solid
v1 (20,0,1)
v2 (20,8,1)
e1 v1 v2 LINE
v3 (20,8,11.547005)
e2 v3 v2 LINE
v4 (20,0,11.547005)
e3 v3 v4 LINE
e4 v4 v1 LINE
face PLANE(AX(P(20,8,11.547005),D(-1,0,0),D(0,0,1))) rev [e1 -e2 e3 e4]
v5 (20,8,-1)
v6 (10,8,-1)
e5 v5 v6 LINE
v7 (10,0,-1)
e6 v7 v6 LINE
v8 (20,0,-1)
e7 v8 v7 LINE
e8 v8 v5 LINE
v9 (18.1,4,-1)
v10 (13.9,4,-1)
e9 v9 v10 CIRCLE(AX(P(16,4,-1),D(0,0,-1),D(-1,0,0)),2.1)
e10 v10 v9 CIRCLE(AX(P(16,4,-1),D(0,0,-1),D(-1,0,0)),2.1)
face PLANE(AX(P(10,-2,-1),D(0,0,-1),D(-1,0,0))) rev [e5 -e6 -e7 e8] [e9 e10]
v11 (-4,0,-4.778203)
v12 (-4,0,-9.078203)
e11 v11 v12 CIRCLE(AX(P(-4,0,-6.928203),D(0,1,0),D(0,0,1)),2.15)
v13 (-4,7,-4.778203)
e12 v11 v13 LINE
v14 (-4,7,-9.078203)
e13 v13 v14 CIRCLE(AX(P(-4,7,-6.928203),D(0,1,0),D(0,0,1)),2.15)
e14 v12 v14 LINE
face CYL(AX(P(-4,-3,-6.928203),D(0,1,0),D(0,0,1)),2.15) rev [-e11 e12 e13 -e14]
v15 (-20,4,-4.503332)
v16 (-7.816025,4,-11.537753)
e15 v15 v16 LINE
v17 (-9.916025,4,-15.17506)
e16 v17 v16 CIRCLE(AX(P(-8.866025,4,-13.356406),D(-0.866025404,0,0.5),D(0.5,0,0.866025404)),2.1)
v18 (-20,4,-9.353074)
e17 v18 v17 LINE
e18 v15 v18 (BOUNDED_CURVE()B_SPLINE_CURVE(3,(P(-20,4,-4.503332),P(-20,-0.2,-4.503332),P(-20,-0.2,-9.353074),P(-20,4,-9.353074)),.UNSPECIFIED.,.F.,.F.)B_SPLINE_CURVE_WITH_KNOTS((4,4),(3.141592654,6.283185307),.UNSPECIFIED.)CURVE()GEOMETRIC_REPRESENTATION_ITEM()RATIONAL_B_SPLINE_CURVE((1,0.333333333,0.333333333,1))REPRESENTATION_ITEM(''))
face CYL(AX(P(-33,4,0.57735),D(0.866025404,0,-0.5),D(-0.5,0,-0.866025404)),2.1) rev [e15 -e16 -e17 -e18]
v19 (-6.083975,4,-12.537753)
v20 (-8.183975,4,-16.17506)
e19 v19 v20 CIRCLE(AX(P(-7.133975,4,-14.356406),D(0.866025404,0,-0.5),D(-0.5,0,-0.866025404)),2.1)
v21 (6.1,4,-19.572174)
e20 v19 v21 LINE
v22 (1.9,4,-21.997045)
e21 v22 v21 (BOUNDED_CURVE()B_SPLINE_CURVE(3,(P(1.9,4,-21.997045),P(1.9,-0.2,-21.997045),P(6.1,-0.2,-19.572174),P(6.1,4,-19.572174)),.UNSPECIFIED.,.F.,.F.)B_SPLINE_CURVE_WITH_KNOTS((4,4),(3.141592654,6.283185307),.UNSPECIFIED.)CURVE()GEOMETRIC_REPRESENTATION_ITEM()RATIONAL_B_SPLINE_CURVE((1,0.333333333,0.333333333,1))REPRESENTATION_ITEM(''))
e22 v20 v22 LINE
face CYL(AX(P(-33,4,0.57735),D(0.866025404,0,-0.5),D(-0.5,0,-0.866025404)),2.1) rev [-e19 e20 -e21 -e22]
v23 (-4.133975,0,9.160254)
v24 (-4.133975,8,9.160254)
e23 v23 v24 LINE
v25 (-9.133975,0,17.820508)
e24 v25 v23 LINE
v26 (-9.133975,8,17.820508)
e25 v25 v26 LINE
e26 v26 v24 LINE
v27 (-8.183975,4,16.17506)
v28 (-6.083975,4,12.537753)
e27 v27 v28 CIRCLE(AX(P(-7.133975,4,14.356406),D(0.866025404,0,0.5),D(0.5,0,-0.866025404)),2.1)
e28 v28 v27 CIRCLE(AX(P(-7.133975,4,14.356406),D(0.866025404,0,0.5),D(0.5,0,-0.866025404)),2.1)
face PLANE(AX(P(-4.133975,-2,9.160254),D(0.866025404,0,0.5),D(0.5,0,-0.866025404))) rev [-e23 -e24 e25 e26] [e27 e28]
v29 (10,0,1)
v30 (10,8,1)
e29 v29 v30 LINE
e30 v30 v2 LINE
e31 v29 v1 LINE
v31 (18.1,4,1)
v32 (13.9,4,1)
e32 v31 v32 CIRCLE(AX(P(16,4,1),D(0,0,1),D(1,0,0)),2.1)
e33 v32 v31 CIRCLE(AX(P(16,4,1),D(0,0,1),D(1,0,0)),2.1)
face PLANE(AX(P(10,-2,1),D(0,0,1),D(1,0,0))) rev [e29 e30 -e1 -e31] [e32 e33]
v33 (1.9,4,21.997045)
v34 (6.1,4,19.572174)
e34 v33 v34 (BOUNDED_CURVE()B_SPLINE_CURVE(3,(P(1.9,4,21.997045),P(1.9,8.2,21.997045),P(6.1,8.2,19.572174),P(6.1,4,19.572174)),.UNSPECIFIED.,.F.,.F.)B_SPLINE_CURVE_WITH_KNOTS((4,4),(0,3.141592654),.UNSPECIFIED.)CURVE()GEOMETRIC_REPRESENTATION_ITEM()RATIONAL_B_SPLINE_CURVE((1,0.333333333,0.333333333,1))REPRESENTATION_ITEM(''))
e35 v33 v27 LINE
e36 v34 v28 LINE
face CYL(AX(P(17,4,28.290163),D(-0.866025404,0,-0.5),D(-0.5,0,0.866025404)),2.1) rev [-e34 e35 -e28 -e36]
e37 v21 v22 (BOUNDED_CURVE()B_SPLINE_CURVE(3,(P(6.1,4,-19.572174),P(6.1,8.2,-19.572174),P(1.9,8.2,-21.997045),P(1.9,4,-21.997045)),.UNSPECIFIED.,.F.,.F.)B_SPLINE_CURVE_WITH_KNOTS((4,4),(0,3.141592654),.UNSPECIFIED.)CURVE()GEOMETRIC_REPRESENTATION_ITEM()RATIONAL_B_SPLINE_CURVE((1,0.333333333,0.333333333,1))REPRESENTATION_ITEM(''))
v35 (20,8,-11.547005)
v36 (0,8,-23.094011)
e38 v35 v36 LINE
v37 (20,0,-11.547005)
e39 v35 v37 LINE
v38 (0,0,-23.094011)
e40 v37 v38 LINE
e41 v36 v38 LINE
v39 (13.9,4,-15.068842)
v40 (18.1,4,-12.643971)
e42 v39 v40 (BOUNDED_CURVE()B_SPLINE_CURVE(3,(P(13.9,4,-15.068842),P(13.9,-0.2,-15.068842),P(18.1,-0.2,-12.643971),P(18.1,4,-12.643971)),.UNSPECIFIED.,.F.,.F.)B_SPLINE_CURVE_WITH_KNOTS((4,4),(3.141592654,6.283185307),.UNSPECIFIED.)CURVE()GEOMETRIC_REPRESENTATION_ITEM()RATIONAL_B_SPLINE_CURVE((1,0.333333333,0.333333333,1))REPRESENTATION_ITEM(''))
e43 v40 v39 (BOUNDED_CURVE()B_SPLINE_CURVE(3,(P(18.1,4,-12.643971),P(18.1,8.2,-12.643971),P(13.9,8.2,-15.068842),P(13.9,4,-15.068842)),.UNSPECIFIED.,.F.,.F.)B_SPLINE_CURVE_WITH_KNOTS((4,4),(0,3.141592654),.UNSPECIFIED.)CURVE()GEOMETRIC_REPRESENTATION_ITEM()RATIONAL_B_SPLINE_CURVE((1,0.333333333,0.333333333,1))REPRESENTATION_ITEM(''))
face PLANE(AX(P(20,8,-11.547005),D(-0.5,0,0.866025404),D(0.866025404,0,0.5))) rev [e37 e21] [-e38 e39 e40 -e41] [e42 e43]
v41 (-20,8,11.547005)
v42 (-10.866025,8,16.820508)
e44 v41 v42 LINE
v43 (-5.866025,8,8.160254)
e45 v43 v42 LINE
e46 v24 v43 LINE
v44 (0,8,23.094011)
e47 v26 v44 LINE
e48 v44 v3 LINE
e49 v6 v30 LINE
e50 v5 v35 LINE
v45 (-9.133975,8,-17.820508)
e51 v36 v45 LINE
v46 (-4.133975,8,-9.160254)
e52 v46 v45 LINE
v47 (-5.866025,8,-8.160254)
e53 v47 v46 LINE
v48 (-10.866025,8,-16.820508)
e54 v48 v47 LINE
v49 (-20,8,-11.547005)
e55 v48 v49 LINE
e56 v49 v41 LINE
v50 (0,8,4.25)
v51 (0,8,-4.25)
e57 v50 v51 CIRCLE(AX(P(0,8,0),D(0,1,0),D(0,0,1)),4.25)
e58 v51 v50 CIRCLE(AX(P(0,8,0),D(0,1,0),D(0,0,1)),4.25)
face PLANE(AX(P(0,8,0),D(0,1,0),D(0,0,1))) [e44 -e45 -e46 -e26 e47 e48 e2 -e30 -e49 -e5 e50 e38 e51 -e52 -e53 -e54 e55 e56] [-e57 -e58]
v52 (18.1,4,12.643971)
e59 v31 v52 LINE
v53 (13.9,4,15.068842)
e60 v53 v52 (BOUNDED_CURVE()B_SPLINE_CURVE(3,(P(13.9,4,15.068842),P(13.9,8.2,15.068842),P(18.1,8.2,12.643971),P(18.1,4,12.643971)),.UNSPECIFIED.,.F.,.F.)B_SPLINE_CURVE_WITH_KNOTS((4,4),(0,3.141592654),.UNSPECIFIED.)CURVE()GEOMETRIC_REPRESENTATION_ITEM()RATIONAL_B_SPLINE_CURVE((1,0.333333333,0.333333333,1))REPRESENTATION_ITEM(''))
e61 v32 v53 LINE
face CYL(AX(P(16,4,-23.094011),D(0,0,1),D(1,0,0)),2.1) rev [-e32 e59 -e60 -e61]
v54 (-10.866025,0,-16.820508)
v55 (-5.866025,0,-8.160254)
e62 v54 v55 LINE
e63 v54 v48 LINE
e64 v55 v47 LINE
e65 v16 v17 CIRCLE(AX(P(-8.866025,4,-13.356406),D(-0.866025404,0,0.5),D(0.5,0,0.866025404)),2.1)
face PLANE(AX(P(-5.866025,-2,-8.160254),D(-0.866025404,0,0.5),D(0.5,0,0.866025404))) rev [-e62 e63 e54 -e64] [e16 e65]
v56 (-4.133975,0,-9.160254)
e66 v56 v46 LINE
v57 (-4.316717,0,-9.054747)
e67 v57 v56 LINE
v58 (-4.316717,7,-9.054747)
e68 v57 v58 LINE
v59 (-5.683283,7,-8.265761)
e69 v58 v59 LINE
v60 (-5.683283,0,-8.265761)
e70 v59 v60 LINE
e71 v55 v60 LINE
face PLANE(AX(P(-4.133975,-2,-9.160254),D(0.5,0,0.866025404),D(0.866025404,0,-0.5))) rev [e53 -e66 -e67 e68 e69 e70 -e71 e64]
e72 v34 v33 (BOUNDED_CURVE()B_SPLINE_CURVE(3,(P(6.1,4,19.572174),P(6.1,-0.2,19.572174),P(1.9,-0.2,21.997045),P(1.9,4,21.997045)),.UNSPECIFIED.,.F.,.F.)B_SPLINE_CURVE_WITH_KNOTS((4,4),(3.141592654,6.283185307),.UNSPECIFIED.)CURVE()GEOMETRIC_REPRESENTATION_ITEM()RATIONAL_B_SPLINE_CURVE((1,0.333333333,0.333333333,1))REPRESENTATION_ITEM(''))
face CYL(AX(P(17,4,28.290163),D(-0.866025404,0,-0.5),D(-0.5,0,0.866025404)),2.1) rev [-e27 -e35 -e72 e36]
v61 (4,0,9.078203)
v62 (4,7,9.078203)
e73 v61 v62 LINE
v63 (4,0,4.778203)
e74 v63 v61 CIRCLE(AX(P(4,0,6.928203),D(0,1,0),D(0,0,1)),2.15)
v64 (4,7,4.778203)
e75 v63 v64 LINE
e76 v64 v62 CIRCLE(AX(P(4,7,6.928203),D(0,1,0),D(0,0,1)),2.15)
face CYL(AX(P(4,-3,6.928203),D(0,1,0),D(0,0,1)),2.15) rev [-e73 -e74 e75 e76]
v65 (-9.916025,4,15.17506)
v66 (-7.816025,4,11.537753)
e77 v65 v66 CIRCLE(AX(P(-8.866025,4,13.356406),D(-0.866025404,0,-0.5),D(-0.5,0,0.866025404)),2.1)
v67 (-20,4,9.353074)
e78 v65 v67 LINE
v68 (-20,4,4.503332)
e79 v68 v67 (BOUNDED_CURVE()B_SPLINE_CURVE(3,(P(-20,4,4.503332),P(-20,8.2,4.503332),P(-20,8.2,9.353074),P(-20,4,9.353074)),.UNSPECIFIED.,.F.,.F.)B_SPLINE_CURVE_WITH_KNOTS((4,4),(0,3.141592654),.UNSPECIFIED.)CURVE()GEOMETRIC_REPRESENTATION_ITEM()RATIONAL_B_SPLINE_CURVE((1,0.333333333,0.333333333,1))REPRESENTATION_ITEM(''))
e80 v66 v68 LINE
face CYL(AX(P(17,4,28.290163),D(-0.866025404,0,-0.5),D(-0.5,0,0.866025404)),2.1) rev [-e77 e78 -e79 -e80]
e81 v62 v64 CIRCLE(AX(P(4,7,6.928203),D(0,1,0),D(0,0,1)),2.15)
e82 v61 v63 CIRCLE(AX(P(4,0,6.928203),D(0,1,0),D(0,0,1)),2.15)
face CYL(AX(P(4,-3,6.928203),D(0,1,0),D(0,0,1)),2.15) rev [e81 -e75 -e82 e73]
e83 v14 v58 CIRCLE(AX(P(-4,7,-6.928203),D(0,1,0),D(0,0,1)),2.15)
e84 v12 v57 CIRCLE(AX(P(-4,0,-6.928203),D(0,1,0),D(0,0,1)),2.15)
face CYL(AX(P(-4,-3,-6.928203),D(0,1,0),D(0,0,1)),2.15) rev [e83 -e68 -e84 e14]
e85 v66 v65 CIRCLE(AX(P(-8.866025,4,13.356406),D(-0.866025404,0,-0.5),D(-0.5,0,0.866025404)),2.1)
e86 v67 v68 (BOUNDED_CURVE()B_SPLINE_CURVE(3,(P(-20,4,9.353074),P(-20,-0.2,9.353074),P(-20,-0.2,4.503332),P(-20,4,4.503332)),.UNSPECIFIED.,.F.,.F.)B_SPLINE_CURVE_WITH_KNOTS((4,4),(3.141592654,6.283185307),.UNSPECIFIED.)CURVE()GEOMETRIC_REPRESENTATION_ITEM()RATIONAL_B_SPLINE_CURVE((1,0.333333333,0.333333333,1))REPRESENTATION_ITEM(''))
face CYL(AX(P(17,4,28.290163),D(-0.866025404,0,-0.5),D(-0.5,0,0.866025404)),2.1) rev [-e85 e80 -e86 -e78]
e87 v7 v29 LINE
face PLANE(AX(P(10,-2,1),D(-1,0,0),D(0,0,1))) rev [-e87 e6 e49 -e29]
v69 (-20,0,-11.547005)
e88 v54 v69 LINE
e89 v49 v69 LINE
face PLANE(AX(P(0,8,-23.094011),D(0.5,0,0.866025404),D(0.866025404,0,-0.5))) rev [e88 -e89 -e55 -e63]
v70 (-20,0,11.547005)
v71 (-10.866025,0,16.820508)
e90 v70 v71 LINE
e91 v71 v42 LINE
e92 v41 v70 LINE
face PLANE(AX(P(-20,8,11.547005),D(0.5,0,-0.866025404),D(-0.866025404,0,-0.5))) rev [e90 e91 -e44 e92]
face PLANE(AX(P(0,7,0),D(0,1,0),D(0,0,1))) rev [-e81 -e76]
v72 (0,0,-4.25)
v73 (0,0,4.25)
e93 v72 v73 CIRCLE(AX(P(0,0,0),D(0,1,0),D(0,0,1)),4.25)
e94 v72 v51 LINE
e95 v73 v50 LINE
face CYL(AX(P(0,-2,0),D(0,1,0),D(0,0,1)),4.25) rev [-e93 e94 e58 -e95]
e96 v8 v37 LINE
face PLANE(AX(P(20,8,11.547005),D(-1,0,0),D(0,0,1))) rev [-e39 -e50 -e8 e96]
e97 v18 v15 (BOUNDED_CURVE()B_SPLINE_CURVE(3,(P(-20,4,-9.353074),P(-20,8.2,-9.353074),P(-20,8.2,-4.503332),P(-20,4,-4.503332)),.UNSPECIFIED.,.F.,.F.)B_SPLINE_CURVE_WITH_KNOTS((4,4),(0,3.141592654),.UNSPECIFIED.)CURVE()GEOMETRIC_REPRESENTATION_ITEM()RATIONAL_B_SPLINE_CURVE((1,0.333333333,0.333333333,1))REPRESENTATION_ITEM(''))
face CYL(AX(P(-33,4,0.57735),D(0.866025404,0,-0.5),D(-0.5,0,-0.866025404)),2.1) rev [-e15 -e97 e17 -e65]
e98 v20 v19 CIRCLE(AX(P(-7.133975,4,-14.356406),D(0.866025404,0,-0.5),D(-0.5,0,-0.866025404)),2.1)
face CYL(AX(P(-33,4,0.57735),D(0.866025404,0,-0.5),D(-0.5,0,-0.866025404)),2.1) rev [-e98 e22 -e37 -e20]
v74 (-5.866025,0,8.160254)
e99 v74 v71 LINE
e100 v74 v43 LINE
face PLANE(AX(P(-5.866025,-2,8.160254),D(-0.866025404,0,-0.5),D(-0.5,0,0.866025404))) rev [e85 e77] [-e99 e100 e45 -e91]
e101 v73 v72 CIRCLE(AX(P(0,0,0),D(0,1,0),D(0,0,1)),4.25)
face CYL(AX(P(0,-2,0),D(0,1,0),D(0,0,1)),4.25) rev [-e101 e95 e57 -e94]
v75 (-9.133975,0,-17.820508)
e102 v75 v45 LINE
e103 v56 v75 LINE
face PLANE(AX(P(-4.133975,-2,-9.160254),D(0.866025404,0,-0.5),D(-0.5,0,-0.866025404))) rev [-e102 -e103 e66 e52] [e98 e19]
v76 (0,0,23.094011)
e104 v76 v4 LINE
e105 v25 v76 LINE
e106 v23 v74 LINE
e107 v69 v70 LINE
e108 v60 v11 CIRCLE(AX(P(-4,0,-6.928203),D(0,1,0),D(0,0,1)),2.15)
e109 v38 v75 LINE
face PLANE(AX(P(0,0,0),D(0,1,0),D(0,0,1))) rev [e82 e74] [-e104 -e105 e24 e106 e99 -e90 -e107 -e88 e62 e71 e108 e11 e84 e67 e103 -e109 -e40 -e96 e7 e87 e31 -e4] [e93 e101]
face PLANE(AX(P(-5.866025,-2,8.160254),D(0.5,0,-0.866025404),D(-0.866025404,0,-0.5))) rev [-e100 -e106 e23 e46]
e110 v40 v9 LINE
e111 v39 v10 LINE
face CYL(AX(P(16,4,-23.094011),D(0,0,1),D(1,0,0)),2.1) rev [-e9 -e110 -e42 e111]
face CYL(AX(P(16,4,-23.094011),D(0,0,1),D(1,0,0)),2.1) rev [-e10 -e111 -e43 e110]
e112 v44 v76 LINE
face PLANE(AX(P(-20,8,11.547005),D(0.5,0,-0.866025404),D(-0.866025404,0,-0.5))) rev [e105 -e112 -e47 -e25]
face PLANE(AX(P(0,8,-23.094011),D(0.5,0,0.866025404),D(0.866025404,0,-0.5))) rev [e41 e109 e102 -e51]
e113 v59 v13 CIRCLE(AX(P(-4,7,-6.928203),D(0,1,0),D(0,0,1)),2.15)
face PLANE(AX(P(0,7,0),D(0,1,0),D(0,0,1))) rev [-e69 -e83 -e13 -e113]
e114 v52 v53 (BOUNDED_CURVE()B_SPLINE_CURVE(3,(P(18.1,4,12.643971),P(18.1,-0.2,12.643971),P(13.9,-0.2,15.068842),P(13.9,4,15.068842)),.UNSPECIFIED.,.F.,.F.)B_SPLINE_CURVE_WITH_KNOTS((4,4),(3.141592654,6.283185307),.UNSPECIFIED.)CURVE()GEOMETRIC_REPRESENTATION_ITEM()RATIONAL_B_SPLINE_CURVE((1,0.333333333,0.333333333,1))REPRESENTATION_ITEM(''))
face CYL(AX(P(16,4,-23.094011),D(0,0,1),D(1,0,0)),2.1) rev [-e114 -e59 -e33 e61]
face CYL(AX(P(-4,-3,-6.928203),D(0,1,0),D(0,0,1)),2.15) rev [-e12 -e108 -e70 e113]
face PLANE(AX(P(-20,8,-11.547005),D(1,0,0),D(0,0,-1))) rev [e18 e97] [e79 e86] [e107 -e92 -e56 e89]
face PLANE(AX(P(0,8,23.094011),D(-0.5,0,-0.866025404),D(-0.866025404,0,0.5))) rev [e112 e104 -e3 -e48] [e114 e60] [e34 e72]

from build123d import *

# Parameters (mm, degrees)
BOSS_EXTRUDE1_DEPTH = 8
SKETCH2_R           = 4.25
CUT_EXTRUDE1_DEPTH  = 10
CUT_EXTRUDE3_DEPTH  = 10
CIRPATTERN1_COUNT   = 3
SKETCH4_R           = 2.1
CUT_EXTRUDE4_DEPTH  = 33.3190556
CIRPATTERN2_COUNT   = 3
SKETCH6_R           = 2.15
CUT_EXTRUDE6_DEPTH  = 10


with BuildPart() as part:
    # Sketch1 → Boss-Extrude1 (new body)
    with BuildSketch(Plane(origin=(0, 0, 0), x_dir=(1, 0, 0), z_dir=(0, 1, 0))):
        Polygon((0, 23.094010768), (-20, 11.547005384), (-20, -11.547005384), (0, -23.094010768), (20, -11.547005384), (20, 11.547005384), align=None)
    extrude(amount=BOSS_EXTRUDE1_DEPTH)

    # Sketch2 → Cut-Extrude1 (cut)
    with BuildSketch(Plane(origin=(0, 8, 0), x_dir=(1, 0, 0), z_dir=(0, 1, 0))):
        with Locations(Location((0, 0, 0), (0, 0, 270))):
            Circle(SKETCH2_R)
    extrude(amount=-CUT_EXTRUDE1_DEPTH, mode=Mode.SUBTRACT)

    # Sketch3 → Cut-Extrude3 (cut)
    with BuildSketch(Plane(origin=(0, 8, 0), x_dir=(1, 0, 0), z_dir=(0, 1, 0))):
        Polygon((-9.133974596, 17.820508076), (-10.866025404, 16.820508076), (-5.866025404, 8.160254038), (-4.133974596, 9.160254038), align=None)
    cut_extrude3 = extrude(amount=-CUT_EXTRUDE3_DEPTH, mode=Mode.SUBTRACT)

    # CirPattern1: Cut-Extrude3 ×3 about axis
    cirpattern1_axis = Axis((0, 0, 0), (0, 1, 0))
    for i in range(1, CIRPATTERN1_COUNT):
        add(cut_extrude3.rotate(cirpattern1_axis, i * 360 / CIRPATTERN1_COUNT), mode=Mode.SUBTRACT)

    # Sketch4 → Cut-Extrude4 (cut, symmetric)
    with BuildSketch(Plane.XY.offset(-1)):
        with Locations((16, 4)):
            Circle(SKETCH4_R)
    cut_extrude4 = extrude(amount=CUT_EXTRUDE4_DEPTH, both=True, mode=Mode.SUBTRACT)

    # CirPattern2: Cut-Extrude4 ×3 about axis
    cirpattern2_axis = Axis((0, -2, 0), (0, 1, 0))
    for i in range(1, CIRPATTERN2_COUNT):
        add(cut_extrude4.rotate(cirpattern2_axis, i * 360 / CIRPATTERN2_COUNT), mode=Mode.SUBTRACT)

    # Sketch6 → Cut-Extrude6 (cut)
    with BuildSketch(Plane(origin=(-14.906511483, 7, 5.40190095), x_dir=(1, 0, 0), z_dir=(0, 1, 0))):
        with Locations((10.906511483, 12.330104181)):
            Circle(SKETCH6_R)
        with Locations(Location((18.906511483, -1.52630228, 0), (0, 0, 270))):
            Circle(SKETCH6_R)
    extrude(amount=-CUT_EXTRUDE6_DEPTH, mode=Mode.SUBTRACT)


solid = part.part
